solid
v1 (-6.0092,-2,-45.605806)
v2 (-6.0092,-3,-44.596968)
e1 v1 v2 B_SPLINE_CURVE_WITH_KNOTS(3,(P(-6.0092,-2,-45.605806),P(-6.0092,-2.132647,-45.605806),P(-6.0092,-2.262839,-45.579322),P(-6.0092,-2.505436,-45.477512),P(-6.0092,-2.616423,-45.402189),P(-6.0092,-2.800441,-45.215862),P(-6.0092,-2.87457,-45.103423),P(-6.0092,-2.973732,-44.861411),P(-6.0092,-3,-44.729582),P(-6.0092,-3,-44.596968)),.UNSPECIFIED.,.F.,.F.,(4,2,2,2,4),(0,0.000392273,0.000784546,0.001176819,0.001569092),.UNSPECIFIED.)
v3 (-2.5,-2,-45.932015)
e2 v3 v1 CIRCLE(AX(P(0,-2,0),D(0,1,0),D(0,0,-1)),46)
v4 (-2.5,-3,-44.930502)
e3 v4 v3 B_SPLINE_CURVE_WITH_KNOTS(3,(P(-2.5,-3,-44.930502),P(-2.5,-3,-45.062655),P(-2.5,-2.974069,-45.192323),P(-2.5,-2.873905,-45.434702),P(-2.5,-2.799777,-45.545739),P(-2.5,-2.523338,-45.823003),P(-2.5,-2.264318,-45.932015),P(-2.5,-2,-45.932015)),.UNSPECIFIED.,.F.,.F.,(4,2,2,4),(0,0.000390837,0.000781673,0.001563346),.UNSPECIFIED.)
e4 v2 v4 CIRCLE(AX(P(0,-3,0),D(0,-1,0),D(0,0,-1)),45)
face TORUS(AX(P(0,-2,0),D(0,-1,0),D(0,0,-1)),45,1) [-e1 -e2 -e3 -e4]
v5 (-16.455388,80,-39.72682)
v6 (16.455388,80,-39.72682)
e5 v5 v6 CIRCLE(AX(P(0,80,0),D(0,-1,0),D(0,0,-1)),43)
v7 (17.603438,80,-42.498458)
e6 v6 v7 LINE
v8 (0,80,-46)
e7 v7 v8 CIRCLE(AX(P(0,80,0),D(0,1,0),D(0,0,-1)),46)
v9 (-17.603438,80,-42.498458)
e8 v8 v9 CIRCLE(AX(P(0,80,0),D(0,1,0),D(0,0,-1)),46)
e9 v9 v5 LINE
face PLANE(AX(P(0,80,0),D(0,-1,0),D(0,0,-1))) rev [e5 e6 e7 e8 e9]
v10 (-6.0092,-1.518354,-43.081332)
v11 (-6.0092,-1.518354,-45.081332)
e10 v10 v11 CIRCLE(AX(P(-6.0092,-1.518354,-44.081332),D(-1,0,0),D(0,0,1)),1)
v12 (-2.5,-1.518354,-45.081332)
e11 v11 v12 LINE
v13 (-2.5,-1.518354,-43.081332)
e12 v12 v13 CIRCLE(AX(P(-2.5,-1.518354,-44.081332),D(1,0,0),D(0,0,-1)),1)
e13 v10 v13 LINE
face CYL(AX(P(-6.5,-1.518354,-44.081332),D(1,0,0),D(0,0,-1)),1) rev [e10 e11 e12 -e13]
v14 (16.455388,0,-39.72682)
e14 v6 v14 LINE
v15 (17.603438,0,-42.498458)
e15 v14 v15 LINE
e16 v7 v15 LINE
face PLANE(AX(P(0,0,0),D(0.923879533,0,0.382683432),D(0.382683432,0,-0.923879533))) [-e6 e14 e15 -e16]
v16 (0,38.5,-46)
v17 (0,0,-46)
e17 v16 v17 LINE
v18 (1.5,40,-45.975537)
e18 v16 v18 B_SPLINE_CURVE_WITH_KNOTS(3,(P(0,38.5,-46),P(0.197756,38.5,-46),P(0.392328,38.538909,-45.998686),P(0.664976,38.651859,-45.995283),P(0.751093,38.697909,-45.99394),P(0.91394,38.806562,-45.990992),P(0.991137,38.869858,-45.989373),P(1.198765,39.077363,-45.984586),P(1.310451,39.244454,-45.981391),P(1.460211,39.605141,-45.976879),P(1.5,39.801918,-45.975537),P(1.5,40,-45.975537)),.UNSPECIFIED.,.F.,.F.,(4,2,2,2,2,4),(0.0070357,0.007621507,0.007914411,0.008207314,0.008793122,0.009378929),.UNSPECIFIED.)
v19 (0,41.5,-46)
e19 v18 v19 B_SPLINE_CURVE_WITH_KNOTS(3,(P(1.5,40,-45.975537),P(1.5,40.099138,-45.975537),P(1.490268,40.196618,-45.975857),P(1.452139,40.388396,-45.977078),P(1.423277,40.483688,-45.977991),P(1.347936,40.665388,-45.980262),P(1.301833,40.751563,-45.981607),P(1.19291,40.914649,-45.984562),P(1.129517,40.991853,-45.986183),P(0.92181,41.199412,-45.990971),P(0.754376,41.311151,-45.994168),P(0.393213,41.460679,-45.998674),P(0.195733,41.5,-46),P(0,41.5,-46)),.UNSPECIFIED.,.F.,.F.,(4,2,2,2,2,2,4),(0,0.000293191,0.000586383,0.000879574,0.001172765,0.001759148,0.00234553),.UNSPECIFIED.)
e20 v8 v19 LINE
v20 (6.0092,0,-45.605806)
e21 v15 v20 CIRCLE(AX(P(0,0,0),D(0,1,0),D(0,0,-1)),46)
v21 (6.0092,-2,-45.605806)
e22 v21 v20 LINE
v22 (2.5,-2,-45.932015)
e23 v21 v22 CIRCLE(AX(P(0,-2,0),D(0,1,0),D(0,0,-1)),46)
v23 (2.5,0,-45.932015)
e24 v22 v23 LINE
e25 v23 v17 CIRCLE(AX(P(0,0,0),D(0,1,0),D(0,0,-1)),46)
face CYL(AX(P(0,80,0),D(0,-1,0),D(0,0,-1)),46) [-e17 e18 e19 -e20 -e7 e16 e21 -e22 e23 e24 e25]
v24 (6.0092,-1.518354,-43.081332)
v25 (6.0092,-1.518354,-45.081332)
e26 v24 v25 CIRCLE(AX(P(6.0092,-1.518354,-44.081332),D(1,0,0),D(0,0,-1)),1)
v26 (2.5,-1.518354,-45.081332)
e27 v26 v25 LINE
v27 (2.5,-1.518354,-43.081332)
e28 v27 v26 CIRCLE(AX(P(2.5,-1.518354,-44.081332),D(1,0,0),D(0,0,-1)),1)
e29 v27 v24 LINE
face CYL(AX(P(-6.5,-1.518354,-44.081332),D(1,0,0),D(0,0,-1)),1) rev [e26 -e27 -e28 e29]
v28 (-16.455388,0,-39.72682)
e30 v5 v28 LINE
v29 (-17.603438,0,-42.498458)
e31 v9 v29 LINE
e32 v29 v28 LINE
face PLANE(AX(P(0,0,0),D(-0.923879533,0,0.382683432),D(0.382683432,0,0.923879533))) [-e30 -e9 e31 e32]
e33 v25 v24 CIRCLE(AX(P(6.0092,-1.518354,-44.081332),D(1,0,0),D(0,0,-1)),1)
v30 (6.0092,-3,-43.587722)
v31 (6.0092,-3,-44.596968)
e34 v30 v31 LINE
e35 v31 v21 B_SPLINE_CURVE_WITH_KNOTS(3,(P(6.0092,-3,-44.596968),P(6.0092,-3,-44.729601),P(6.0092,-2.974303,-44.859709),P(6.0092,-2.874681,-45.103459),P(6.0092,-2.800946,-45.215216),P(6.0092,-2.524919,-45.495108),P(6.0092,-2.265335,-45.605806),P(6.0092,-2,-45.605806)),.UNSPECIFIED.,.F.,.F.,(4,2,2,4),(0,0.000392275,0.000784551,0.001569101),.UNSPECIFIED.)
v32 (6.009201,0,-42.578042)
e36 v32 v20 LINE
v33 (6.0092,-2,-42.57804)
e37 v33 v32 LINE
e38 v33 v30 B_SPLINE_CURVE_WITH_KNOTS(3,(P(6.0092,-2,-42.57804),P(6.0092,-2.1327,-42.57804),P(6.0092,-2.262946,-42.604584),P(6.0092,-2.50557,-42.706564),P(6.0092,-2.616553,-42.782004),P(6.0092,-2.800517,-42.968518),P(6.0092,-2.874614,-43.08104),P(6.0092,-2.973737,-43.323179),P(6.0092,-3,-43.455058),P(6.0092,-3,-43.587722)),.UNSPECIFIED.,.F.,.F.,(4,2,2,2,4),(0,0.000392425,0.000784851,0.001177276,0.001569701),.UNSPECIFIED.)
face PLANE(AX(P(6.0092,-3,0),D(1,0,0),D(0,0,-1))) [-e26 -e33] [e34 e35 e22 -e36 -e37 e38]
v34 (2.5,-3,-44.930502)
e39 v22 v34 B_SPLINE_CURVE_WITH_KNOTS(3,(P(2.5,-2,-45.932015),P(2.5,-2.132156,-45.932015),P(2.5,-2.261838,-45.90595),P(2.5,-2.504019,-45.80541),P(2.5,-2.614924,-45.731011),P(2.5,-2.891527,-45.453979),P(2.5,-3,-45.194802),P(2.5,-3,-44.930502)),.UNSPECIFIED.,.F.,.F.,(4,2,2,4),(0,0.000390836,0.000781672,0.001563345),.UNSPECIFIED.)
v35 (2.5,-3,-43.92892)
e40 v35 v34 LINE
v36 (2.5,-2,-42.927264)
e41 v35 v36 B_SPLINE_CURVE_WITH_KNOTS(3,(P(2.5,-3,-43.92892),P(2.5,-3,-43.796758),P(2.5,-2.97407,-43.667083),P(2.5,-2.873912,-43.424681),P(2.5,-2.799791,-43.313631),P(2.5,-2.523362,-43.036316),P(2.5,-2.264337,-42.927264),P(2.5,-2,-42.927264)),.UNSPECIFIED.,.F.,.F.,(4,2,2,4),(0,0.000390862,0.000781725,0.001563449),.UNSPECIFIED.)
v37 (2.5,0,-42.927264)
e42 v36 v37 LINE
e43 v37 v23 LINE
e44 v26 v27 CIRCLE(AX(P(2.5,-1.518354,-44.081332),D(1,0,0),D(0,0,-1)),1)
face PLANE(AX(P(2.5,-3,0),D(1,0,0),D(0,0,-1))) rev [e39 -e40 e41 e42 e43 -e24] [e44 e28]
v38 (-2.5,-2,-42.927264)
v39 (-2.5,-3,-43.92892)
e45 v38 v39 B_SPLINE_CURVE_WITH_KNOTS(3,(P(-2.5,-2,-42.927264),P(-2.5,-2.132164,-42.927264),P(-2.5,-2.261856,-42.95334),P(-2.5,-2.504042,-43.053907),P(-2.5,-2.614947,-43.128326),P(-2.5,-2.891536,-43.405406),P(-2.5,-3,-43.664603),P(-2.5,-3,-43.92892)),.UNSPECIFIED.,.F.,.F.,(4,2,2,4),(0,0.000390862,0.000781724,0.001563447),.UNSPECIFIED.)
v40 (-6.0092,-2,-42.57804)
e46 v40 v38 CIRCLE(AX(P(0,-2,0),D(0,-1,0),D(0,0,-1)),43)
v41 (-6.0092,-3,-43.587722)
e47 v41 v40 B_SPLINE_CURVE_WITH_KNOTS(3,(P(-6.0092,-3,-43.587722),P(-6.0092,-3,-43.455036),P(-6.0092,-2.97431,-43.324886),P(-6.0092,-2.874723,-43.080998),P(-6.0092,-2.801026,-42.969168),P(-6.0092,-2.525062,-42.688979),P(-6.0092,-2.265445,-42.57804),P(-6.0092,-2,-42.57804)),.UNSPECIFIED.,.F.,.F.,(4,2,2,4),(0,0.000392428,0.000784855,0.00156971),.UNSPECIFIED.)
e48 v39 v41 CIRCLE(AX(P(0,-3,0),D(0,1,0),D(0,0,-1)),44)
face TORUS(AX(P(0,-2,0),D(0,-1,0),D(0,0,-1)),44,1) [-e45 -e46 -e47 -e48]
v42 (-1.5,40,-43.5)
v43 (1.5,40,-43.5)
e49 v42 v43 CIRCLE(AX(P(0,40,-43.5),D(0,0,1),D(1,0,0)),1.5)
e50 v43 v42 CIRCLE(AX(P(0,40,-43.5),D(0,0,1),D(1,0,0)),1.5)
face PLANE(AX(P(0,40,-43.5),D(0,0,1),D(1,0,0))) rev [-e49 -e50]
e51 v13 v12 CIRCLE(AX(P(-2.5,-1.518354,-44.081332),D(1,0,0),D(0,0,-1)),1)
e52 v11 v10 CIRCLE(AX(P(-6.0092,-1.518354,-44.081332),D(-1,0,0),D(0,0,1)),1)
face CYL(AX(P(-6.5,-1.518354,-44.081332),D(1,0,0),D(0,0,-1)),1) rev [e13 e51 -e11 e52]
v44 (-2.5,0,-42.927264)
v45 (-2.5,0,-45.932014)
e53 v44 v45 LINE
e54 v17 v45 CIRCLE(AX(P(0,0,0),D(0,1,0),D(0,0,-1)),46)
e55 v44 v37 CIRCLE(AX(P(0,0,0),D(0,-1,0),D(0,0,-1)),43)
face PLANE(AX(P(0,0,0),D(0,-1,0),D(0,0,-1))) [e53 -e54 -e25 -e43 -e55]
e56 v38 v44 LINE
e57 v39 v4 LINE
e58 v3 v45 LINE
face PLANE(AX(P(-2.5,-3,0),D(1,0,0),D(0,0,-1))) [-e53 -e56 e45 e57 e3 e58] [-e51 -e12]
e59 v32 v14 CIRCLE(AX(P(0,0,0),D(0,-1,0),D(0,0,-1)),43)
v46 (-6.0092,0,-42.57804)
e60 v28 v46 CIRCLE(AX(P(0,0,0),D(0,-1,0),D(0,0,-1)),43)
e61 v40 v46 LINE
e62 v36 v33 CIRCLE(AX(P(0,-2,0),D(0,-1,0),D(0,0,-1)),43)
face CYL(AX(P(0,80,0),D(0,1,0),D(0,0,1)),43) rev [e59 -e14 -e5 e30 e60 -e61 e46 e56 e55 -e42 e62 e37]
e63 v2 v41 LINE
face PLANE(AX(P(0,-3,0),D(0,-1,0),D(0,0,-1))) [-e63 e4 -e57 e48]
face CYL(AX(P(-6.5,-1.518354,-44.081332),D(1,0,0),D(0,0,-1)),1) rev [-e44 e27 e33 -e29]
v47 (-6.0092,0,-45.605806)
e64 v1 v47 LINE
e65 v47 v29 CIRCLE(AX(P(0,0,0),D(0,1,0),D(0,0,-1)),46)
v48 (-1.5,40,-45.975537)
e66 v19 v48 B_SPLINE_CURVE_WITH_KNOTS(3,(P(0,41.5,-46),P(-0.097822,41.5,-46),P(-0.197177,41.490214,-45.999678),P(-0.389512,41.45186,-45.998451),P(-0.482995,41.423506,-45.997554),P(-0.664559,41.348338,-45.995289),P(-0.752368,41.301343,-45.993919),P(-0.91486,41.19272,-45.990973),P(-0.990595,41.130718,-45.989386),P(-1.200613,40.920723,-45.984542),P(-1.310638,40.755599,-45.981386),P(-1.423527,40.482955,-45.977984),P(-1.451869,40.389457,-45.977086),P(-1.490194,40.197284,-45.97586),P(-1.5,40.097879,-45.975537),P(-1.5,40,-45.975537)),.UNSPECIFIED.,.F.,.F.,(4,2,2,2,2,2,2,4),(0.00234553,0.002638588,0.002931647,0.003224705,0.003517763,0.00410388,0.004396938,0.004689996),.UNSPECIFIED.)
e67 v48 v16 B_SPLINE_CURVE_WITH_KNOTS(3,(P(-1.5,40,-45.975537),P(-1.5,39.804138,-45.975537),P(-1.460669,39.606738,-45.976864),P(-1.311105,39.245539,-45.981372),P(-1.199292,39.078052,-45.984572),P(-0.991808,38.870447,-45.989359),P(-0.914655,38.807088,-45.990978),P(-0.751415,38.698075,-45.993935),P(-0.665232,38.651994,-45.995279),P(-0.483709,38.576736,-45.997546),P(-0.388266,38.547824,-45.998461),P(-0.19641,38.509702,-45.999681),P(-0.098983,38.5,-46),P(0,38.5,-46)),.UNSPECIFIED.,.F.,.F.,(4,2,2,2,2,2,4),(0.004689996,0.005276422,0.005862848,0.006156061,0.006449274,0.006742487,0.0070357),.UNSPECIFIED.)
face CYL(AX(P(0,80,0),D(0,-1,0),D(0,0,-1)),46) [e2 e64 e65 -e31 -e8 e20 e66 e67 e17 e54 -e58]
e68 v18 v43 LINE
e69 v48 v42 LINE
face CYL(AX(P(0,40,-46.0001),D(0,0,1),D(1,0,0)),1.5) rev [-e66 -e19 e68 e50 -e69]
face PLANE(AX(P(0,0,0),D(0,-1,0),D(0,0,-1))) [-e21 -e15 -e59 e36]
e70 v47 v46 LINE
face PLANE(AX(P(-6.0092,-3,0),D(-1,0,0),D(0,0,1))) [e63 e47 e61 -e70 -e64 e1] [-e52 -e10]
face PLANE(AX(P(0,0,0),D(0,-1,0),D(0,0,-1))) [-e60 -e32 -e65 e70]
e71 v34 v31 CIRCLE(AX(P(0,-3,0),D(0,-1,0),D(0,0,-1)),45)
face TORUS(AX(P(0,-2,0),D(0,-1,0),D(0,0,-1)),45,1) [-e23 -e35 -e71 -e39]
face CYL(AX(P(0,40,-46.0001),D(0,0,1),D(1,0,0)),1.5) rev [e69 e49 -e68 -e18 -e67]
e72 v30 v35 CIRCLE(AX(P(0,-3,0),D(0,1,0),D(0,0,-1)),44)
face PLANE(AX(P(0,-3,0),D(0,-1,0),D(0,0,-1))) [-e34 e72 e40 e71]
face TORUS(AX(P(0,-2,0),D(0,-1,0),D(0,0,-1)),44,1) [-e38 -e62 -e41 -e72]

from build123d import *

# Parameters (mm, degrees)
EXTRUDE_1_DEPTH     = 3
SKETCH_7_R          = 1
CUT_EXTRUDE_2_DEPTH = 6.5
FILLET_3_R          = 1
CUT_EXTRUDE_START   = -43.5
SKETCH_8_R          = 1.5
CUT_EXTRUDE_3_DEPTH = 51.446160402


with BuildPart() as part:
    # 草图4 for 放样1 → 放样1 section 0
    with BuildSketch(Plane(origin=(0, 80, 0), x_dir=(1, 0, 0), z_dir=(0, 1, 0))):
        with BuildLine():
            Line((-17.603437889, 42.498458496), (-16.455387592, 39.726819898))
            # circular arc as an exact rational Bezier (weights 1, cos(half-angle), 1)
            Bezier((-16.455387592, 39.726819898), (0, 46.542864613), (16.455387592, 39.726819898), weights=[1, 0.923879533, 1])
            Line((16.455387592, 39.726819898), (17.603437889, 42.498458496))
            Bezier((17.603437889, 42.498458496), (0, 49.790041213), (-17.603437889, 42.498458496), weights=[1, 0.923879533, 1])
        make_face()
    # 草图3 for 放样1 → 放样1 section 1
    with BuildSketch(Plane(origin=(0, 0, 0), x_dir=(1, 0, 0), z_dir=(0, 1, 0))):
        with BuildLine():
            Line((-17.603437889, 42.498458496), (-16.455387592, 39.726819898))
            Bezier((-16.455387592, 39.726819898), (0, 46.542864613), (16.455387592, 39.726819898), weights=[1, 0.923879533, 1])
            Line((16.455387592, 39.726819898), (17.603437889, 42.498458496))
            Bezier((17.603437889, 42.498458496), (0, 49.790041213), (-17.603437889, 42.498458496), weights=[1, 0.923879533, 1])
        make_face()
    loft()

    # 草图6 → 凸台-拉伸1 (add)
    with BuildSketch(Plane.XZ):
        with BuildLine():
            Line((-6.009200316, -42.57804025), (-6.009200316, -45.605805678))
            ThreePointArc((-6.009200316, -45.605805678), (-4.257725406, -45.802530218), (-2.5, -45.932014979))
            Line((-2.5, -45.932014979), (-2.5, -42.927264064))
            ThreePointArc((-2.5, -42.927264064), (-4.258181751, -42.788642046), (-6.009200316, -42.57804025))
        make_face()
        with BuildLine():
            ThreePointArc((2.5, -45.932014979), (4.257725406, -45.802530218), (6.009200316, -45.605805678))
            Line((6.009200316, -45.605805678), (6.009200316, -42.57804025))
            ThreePointArc((6.009200316, -42.57804025), (4.258181751, -42.788642046), (2.5, -42.927264064))
            Line((2.5, -42.927264064), (2.5, -45.932014979))
        make_face()
    extrude(amount=EXTRUDE_1_DEPTH)

    # 草图7 → 切除-拉伸2 (cut, symmetric)
    with BuildSketch(Plane(origin=(0, 0, 0), x_dir=(0, 0, -1), z_dir=(1, 0, 0))):
        with Locations((44.081332421, -1.518353576)):
            Circle(SKETCH_7_R)
    extrude(amount=CUT_EXTRUDE_2_DEPTH, both=True, mode=Mode.SUBTRACT)

    # 圆角3
    fillet_3_edges = [part.edges().sort_by_distance(p)[0] for p in [
        (4.257725406, -3, -45.802530218),
        (4.258181751, -3, -42.788642046),
        (-4.257725406, -3, -45.802530218),
        (-4.258181751, -3, -42.788642046),
    ]]
    fillet(fillet_3_edges, radius=FILLET_3_R)

    # 草图8 → 切除-拉伸3 (cut, through all)
    with BuildSketch(Plane.XY.offset(CUT_EXTRUDE_START)):
        with Locations((0, 40)):
            Circle(SKETCH_8_R)
    extrude(amount=-CUT_EXTRUDE_3_DEPTH, mode=Mode.SUBTRACT)


solid = part.part
